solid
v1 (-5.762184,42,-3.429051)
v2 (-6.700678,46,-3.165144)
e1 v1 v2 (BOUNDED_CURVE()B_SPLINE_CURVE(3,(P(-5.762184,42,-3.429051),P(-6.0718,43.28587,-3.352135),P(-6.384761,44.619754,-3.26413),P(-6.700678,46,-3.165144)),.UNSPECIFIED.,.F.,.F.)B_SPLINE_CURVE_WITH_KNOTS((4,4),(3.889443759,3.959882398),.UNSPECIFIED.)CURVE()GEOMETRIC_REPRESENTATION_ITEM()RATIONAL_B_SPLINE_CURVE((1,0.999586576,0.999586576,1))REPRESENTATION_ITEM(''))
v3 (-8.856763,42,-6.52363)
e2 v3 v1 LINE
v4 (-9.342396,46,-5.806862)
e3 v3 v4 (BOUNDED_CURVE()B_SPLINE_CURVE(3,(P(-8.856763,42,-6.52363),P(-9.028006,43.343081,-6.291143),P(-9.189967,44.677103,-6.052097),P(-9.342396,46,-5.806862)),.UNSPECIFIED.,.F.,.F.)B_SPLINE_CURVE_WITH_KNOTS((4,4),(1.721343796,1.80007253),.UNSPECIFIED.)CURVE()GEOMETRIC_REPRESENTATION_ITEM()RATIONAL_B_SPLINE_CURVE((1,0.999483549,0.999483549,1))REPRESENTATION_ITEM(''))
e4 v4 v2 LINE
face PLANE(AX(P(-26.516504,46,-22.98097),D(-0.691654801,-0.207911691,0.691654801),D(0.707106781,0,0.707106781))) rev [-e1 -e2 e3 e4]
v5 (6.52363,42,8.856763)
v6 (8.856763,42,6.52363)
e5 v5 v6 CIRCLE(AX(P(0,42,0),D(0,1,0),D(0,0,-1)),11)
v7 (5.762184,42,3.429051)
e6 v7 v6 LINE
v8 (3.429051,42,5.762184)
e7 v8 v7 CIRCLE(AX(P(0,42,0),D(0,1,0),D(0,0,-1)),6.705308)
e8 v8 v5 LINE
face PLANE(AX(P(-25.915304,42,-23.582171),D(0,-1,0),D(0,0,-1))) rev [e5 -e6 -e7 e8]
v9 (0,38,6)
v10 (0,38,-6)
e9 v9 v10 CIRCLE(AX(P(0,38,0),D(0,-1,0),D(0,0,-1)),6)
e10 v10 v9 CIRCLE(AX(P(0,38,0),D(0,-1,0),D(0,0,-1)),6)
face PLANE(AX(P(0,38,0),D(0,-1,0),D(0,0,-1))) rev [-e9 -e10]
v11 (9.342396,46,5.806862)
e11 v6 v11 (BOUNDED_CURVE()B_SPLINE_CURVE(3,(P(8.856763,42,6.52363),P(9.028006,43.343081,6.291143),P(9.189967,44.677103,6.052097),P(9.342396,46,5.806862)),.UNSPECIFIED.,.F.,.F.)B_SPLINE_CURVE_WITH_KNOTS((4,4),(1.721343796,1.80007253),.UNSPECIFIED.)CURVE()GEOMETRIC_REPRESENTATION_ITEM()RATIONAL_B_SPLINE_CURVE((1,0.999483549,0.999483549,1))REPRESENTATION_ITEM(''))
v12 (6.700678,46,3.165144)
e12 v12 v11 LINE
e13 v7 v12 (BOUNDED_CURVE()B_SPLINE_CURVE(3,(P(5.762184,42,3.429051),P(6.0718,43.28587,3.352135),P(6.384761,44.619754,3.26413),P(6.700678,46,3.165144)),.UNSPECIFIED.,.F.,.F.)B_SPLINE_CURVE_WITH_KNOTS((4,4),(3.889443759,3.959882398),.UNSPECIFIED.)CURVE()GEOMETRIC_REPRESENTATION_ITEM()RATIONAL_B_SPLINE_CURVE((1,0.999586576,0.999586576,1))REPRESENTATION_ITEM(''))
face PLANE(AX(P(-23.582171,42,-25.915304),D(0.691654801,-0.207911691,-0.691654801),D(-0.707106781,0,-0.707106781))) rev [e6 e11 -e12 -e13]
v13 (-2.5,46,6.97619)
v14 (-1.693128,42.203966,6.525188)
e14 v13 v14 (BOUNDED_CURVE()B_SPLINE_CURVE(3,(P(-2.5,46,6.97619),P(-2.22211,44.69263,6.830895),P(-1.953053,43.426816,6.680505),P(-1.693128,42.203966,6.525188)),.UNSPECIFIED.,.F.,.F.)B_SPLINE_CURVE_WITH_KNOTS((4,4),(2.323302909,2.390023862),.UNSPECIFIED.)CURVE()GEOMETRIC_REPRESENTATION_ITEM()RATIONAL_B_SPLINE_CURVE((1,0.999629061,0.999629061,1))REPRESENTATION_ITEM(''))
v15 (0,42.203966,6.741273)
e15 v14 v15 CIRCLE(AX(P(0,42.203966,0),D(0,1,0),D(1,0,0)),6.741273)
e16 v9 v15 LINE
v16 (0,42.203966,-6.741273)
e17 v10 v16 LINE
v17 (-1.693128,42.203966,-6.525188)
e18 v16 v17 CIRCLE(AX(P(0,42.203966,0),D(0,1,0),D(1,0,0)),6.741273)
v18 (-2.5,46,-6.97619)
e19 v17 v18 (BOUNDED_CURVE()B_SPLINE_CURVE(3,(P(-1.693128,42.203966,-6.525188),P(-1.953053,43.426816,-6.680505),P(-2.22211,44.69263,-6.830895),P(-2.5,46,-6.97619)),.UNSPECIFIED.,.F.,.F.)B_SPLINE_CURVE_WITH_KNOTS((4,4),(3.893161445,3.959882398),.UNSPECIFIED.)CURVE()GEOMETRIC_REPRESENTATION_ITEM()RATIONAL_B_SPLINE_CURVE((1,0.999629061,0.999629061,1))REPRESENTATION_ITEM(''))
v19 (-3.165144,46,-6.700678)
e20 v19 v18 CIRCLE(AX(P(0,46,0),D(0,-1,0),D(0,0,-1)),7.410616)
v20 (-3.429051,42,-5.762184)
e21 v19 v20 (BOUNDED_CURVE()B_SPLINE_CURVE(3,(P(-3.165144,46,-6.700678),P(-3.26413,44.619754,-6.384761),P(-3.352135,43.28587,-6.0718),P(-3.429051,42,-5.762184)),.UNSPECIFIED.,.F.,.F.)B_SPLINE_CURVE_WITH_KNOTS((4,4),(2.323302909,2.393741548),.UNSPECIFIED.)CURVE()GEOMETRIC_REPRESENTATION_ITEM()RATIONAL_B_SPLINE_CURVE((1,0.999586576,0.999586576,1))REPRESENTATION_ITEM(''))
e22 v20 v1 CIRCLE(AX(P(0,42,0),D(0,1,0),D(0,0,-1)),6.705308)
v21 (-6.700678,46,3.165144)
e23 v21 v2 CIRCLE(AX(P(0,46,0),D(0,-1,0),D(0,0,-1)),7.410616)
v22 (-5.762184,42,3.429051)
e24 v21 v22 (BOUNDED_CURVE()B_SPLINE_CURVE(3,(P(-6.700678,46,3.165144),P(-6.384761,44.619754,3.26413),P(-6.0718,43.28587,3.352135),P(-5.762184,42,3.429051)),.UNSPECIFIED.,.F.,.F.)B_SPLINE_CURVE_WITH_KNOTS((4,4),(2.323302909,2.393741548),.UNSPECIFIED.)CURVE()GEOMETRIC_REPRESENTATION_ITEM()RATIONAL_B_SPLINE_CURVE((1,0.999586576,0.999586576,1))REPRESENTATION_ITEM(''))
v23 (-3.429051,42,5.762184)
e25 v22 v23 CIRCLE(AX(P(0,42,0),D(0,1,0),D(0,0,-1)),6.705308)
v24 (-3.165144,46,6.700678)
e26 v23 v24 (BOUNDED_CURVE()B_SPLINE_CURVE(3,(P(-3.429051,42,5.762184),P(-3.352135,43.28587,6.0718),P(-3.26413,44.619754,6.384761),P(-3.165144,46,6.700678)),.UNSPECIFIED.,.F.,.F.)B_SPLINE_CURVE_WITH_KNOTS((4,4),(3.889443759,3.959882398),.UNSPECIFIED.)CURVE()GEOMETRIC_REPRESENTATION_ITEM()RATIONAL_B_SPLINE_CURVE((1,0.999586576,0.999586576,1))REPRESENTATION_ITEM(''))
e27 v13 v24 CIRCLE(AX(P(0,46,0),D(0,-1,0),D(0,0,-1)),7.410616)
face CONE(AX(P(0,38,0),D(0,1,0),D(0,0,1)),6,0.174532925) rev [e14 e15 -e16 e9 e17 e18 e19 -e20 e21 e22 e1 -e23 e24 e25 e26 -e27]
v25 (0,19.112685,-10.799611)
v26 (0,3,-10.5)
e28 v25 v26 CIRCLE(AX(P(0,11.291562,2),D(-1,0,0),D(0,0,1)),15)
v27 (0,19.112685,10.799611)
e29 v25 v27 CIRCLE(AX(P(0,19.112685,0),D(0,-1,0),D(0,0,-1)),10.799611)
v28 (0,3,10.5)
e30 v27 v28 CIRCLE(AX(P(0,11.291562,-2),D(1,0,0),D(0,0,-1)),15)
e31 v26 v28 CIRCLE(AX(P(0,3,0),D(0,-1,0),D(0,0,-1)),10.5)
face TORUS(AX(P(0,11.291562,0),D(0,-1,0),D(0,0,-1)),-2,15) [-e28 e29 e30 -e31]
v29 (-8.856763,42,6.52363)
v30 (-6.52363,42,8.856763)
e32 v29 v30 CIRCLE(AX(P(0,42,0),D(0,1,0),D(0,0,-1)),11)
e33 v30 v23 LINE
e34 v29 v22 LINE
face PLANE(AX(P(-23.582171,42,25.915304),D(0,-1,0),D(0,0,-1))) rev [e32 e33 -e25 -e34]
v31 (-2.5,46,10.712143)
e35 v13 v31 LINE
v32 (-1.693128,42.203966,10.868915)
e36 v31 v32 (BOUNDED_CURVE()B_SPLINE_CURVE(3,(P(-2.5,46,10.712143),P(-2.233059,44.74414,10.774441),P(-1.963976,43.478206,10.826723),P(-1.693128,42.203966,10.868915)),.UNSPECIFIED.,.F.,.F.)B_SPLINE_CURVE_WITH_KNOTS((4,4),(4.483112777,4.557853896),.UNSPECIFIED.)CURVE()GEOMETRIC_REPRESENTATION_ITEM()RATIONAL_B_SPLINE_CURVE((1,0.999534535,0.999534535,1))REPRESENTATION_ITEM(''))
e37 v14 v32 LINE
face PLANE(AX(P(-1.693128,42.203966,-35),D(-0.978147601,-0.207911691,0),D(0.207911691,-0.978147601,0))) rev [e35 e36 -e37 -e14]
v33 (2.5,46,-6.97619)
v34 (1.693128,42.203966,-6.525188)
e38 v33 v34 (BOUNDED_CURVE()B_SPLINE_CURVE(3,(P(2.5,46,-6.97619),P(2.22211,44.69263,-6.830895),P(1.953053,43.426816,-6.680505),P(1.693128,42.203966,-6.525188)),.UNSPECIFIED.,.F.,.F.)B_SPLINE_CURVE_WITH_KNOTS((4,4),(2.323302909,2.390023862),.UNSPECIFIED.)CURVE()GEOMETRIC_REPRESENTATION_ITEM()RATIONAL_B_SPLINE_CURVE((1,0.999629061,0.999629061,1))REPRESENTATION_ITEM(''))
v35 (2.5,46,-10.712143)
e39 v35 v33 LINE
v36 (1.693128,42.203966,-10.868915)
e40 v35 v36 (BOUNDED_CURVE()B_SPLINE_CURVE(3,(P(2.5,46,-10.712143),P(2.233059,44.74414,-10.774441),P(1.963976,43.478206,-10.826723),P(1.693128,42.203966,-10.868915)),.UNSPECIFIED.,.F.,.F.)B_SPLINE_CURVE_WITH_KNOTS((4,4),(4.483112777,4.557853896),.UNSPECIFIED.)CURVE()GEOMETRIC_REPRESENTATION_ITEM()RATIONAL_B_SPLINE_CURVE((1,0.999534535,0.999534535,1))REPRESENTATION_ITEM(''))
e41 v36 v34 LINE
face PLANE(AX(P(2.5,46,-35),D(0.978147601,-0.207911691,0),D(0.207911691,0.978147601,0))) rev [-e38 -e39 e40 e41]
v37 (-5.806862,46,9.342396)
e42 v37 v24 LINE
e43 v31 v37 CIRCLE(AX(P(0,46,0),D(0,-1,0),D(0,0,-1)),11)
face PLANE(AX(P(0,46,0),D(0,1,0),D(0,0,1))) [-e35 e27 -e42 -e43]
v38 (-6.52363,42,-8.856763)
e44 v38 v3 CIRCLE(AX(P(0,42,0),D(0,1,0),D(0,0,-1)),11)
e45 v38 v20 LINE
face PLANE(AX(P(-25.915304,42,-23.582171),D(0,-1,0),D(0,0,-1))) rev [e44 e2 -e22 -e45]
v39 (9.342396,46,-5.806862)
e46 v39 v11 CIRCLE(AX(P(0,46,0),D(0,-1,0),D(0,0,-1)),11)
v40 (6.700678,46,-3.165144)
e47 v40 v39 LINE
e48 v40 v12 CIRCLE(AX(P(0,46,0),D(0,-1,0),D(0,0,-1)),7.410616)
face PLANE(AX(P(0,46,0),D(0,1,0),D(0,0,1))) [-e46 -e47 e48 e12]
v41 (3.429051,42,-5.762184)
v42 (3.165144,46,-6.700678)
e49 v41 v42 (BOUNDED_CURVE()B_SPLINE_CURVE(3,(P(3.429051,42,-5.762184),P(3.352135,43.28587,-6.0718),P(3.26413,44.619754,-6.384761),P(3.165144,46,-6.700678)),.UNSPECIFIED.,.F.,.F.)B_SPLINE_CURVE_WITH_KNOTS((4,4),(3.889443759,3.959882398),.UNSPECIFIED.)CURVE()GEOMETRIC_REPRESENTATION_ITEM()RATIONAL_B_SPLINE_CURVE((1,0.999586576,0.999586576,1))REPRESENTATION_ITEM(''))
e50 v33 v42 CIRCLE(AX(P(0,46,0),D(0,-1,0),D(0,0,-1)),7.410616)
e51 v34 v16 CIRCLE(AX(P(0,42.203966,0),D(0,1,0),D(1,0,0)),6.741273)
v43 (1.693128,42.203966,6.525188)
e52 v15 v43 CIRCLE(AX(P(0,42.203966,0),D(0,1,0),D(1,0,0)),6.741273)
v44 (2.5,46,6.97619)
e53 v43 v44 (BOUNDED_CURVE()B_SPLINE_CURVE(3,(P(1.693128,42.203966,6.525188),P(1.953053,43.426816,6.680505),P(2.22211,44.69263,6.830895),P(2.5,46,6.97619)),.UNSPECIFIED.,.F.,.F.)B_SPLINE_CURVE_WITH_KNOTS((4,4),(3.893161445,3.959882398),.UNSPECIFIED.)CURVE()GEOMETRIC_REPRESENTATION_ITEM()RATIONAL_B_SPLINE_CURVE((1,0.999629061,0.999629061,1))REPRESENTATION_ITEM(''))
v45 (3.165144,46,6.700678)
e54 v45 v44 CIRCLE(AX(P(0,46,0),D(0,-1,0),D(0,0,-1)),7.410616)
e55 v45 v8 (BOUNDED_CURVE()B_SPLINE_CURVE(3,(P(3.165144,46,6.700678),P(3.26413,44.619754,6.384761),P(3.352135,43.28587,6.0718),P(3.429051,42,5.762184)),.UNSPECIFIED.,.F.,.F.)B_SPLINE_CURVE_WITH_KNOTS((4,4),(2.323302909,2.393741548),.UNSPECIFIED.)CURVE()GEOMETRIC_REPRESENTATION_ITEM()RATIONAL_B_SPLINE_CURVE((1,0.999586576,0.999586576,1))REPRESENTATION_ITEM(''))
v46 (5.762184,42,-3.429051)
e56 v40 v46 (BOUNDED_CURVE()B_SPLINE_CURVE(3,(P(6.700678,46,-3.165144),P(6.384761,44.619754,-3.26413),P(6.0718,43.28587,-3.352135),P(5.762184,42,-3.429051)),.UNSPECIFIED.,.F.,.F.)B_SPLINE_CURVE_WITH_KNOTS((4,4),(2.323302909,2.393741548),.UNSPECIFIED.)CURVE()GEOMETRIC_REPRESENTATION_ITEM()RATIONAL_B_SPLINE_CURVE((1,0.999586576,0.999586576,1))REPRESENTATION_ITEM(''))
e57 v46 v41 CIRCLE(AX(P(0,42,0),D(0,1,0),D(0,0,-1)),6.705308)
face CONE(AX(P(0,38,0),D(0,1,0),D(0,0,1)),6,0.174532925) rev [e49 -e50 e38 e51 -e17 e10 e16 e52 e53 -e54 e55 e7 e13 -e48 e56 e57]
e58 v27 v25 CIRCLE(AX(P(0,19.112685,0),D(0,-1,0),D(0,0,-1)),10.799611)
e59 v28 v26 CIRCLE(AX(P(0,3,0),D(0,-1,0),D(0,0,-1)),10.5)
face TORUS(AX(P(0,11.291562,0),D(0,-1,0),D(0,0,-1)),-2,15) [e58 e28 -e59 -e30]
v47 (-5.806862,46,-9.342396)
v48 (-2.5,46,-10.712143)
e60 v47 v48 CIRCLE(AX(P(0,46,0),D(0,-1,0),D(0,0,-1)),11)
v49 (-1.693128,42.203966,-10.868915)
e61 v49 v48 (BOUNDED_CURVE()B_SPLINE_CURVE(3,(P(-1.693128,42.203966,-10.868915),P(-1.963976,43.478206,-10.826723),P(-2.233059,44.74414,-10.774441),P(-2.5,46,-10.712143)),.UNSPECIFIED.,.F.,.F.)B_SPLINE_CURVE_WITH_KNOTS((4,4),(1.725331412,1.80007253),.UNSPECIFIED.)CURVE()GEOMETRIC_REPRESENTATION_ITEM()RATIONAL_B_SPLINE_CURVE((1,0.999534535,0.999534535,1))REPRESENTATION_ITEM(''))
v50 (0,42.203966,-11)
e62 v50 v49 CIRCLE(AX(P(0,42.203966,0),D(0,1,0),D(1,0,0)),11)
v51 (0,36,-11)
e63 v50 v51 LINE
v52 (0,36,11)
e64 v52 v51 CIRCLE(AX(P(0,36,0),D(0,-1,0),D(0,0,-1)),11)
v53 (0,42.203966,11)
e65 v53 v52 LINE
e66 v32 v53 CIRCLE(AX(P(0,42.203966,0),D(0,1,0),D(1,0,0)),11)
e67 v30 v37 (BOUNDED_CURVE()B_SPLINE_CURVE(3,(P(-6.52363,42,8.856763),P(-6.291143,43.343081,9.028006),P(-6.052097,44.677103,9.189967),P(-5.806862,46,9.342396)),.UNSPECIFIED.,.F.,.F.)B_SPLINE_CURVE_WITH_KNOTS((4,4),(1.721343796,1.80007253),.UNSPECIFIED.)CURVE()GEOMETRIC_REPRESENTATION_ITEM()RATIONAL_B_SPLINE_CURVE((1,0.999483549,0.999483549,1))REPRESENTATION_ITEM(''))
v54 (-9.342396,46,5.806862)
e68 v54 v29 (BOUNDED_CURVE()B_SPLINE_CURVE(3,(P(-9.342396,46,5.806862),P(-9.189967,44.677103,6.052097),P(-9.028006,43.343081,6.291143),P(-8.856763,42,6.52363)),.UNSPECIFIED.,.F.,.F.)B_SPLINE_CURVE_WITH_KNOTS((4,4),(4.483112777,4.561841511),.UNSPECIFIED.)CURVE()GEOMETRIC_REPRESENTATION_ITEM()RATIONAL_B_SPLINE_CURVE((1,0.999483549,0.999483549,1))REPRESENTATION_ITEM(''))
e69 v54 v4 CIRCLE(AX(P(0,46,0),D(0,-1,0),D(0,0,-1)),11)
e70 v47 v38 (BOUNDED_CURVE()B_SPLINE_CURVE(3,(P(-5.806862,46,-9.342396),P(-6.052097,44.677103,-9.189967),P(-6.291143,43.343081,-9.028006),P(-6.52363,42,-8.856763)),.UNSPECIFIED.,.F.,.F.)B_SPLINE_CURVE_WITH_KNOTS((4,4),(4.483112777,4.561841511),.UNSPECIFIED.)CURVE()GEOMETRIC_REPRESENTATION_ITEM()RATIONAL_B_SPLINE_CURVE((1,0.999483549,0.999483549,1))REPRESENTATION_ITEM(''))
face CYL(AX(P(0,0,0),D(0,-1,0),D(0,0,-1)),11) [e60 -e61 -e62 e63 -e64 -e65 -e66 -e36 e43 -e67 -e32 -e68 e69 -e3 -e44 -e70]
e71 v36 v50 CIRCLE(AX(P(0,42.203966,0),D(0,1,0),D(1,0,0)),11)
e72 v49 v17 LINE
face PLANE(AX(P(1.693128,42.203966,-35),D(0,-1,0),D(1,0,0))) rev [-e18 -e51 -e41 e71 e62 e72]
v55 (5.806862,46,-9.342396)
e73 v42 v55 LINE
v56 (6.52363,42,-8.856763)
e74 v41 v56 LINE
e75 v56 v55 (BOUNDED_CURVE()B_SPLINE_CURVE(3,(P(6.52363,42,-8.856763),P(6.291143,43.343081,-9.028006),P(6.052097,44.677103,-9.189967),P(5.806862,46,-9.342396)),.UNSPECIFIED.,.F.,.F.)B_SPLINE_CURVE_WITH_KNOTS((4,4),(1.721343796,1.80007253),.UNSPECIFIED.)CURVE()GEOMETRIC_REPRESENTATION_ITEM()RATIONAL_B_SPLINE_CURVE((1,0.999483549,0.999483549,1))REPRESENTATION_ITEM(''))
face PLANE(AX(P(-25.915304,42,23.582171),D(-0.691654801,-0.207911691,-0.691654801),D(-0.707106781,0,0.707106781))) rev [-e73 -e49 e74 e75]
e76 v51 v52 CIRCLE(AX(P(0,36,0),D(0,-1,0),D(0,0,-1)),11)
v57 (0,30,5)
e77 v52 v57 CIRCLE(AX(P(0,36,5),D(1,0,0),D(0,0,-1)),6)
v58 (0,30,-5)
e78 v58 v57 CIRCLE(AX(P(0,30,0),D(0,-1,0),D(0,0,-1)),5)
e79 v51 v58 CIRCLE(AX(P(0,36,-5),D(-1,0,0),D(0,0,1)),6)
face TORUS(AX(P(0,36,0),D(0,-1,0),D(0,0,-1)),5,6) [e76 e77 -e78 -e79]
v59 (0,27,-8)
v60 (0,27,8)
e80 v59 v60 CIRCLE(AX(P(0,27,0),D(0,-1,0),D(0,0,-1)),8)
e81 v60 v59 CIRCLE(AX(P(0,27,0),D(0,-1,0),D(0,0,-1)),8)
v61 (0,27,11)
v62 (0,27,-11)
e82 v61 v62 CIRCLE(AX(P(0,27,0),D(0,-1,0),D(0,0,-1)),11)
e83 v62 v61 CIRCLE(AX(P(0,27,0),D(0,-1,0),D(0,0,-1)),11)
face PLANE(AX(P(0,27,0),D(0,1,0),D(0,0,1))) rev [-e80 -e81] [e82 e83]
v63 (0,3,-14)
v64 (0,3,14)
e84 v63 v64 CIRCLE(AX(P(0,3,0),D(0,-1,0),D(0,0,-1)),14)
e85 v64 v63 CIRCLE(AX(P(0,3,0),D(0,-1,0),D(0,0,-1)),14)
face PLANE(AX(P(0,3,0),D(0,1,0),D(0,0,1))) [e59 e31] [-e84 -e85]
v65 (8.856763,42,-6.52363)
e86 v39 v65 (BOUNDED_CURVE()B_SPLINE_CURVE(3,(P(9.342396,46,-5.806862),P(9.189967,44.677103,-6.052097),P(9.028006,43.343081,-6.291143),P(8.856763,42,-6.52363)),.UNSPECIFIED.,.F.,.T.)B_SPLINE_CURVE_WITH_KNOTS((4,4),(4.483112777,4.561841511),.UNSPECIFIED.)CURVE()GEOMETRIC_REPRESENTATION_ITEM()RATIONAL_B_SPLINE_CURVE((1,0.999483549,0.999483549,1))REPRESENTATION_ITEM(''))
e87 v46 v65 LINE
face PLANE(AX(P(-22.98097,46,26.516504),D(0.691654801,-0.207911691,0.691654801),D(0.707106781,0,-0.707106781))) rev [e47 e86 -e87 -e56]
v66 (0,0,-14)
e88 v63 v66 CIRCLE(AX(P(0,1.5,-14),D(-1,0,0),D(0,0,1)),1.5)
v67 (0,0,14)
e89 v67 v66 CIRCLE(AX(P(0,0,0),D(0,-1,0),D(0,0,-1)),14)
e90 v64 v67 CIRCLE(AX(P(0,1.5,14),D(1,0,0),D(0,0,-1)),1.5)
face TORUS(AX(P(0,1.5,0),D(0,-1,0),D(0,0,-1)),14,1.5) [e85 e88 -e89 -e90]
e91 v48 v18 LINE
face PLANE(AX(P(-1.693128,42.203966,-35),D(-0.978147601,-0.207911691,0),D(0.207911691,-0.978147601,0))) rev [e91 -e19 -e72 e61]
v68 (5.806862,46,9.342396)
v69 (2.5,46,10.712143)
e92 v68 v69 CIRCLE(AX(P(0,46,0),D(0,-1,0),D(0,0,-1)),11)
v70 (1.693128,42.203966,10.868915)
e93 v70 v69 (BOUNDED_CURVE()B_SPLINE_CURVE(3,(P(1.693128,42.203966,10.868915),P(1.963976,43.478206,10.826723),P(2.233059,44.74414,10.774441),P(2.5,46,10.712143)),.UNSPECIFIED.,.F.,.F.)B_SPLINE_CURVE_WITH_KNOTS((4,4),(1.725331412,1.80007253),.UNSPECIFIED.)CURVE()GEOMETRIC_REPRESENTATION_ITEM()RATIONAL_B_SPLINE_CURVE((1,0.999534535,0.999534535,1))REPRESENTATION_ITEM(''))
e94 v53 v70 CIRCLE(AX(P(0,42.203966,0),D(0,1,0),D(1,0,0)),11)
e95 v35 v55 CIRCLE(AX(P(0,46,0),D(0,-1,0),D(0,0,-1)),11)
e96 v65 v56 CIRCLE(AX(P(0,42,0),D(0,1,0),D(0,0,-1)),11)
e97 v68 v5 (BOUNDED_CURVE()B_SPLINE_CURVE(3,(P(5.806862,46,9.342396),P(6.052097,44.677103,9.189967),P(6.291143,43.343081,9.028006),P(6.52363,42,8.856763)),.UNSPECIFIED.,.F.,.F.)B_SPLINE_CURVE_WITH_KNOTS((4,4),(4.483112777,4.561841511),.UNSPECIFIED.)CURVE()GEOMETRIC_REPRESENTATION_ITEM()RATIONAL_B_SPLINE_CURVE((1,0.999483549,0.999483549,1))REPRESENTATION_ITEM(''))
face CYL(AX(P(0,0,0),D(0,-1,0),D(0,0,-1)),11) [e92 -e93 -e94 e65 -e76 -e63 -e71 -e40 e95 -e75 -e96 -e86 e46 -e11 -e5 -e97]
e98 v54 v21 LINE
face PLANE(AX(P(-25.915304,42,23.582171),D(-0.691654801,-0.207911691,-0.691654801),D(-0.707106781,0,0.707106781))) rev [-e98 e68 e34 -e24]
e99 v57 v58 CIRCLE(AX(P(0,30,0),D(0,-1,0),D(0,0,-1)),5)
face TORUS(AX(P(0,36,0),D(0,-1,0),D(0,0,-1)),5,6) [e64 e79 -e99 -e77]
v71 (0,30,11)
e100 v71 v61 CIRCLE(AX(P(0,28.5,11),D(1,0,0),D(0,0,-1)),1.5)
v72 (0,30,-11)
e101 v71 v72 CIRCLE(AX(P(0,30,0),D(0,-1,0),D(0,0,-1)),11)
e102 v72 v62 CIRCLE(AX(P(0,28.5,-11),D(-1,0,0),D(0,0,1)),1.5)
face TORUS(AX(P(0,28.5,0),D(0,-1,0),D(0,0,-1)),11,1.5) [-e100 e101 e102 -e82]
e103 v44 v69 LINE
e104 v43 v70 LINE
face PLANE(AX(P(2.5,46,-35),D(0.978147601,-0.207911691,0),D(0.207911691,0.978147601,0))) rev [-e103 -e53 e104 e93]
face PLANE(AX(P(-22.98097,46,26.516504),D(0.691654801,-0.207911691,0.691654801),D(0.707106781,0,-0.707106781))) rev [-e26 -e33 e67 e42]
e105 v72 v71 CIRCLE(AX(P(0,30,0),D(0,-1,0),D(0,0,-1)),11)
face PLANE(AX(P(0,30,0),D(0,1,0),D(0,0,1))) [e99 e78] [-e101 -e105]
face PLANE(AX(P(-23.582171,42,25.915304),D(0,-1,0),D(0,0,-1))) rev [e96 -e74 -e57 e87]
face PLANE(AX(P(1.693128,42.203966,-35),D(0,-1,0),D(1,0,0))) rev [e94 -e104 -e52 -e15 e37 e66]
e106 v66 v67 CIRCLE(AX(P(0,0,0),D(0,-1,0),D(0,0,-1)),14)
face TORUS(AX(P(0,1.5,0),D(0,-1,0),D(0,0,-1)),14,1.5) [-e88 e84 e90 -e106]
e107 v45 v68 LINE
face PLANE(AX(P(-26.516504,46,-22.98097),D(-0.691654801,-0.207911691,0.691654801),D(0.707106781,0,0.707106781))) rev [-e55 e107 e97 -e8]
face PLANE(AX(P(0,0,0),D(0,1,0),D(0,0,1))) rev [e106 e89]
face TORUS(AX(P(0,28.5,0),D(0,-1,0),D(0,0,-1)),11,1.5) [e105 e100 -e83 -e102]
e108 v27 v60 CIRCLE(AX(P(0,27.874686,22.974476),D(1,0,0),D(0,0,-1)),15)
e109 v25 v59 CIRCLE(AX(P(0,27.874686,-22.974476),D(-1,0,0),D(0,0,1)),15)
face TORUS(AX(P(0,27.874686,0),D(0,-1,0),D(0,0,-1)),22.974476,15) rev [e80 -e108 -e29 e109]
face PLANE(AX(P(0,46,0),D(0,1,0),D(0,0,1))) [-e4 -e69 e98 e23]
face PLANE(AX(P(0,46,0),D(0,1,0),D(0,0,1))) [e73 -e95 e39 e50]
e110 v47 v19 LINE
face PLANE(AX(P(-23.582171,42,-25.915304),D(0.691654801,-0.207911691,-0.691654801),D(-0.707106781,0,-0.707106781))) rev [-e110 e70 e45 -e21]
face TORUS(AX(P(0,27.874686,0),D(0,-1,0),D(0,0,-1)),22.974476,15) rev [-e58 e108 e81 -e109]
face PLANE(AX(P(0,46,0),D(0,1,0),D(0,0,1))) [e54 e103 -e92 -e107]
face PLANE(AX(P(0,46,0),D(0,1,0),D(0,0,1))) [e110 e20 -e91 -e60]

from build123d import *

# Parameters (mm, degrees)
CRENEL_SLOT_1_DEPTH = 35
CRENEL_SLOT_2_DEPTH = 35
CRENEL_SLOT_3_DEPTH = 35


with BuildPart() as part:
    # Rook Profile Sketch → Rook Body Revolve (revolve)
    with BuildSketch(Plane.XY, mode=Mode.PRIVATE) as rook_body_revolve_sk:
        with BuildLine():
            Line((-14, 0), (0, 0))
            Line((0, 0), (0, 11.291561976))
            Line((0, 11.291561976), (0, 46))
            Line((0, 46), (-11, 46))
            Line((-11, 46), (-11, 36))
            ThreePointArc((-11, 36), (-9.242640687, 31.757359313), (-5, 30))
            Line((-5, 30), (-11, 30))
            ThreePointArc((-11, 30), (-12.5, 28.5), (-11, 27))
            Line((-11, 27), (-8, 27))
            ThreePointArc((-8, 27), (-8.838560173, 22.857127729), (-10.799610921, 19.112684675))
            ThreePointArc((-10.799610921, 19.112684675), (-12.997407444, 11.012689327), (-10.5, 3))
            Line((-10.5, 3), (-14, 3))
            ThreePointArc((-14, 3), (-15.5, 1.5), (-14, 0))
        make_face()
    revolve(rook_body_revolve_sk.sketch.rotate(Axis((0, 0, 0), (0, 1, 0)), 270), axis=Axis((0, 0, 0), (0, 1, 0)))

    # Top Bore Sketch → Top Bore Cut (revolve, cut)
    with BuildSketch(Plane.XY, mode=Mode.PRIVATE) as top_bore_cut_sk:
        Polygon((0, 38), (-6, 38), (-7.410615846, 46), (0, 46), align=None)
    revolve(top_bore_cut_sk.sketch.rotate(Axis((0, 0, 0), (0, 1, 0)), 270), axis=Axis((0, 0, 0), (0, 1, 0)), mode=Mode.SUBTRACT)

    # Crenel Slot 1 Sketch → Crenel Slot 1 (cut, symmetric)
    with BuildSketch(Plane.XY):
        Polygon((-2.5, 46), (2.5, 46), (1.693128152, 42.203966408), (-1.693128152, 42.203966408), align=None)
    extrude(amount=CRENEL_SLOT_1_DEPTH, both=True, mode=Mode.SUBTRACT)

    # Crenel Slot 2 Sketch → Crenel Slot 2 (cut, symmetric)
    with BuildSketch(Plane(origin=(0, 0, 0), x_dir=(-0.7071067811865457, 0, 0.7071067811865493), z_dir=(0.7071067811865493, 0, 0.7071067811865457))):
        Polygon((-2.5, -46), (2.5, -46), (1.649773753, -42), (-1.649773753, -42), align=None)
    extrude(amount=CRENEL_SLOT_2_DEPTH, both=True, mode=Mode.SUBTRACT)

    # Crenel Slot 3 Sketch → Crenel Slot 3 (cut, symmetric)
    with BuildSketch(Plane(origin=(0, 0, 0), x_dir=(0.7071067811865465, 0, 0.7071067811865487), z_dir=(0.7071067811865487, 0, -0.7071067811865465))):
        Polygon((-2.5, -46), (2.5, -46), (1.649773753, -42), (-1.649773753, -42), align=None)
    extrude(amount=CRENEL_SLOT_3_DEPTH, both=True, mode=Mode.SUBTRACT)


solid = part.part
